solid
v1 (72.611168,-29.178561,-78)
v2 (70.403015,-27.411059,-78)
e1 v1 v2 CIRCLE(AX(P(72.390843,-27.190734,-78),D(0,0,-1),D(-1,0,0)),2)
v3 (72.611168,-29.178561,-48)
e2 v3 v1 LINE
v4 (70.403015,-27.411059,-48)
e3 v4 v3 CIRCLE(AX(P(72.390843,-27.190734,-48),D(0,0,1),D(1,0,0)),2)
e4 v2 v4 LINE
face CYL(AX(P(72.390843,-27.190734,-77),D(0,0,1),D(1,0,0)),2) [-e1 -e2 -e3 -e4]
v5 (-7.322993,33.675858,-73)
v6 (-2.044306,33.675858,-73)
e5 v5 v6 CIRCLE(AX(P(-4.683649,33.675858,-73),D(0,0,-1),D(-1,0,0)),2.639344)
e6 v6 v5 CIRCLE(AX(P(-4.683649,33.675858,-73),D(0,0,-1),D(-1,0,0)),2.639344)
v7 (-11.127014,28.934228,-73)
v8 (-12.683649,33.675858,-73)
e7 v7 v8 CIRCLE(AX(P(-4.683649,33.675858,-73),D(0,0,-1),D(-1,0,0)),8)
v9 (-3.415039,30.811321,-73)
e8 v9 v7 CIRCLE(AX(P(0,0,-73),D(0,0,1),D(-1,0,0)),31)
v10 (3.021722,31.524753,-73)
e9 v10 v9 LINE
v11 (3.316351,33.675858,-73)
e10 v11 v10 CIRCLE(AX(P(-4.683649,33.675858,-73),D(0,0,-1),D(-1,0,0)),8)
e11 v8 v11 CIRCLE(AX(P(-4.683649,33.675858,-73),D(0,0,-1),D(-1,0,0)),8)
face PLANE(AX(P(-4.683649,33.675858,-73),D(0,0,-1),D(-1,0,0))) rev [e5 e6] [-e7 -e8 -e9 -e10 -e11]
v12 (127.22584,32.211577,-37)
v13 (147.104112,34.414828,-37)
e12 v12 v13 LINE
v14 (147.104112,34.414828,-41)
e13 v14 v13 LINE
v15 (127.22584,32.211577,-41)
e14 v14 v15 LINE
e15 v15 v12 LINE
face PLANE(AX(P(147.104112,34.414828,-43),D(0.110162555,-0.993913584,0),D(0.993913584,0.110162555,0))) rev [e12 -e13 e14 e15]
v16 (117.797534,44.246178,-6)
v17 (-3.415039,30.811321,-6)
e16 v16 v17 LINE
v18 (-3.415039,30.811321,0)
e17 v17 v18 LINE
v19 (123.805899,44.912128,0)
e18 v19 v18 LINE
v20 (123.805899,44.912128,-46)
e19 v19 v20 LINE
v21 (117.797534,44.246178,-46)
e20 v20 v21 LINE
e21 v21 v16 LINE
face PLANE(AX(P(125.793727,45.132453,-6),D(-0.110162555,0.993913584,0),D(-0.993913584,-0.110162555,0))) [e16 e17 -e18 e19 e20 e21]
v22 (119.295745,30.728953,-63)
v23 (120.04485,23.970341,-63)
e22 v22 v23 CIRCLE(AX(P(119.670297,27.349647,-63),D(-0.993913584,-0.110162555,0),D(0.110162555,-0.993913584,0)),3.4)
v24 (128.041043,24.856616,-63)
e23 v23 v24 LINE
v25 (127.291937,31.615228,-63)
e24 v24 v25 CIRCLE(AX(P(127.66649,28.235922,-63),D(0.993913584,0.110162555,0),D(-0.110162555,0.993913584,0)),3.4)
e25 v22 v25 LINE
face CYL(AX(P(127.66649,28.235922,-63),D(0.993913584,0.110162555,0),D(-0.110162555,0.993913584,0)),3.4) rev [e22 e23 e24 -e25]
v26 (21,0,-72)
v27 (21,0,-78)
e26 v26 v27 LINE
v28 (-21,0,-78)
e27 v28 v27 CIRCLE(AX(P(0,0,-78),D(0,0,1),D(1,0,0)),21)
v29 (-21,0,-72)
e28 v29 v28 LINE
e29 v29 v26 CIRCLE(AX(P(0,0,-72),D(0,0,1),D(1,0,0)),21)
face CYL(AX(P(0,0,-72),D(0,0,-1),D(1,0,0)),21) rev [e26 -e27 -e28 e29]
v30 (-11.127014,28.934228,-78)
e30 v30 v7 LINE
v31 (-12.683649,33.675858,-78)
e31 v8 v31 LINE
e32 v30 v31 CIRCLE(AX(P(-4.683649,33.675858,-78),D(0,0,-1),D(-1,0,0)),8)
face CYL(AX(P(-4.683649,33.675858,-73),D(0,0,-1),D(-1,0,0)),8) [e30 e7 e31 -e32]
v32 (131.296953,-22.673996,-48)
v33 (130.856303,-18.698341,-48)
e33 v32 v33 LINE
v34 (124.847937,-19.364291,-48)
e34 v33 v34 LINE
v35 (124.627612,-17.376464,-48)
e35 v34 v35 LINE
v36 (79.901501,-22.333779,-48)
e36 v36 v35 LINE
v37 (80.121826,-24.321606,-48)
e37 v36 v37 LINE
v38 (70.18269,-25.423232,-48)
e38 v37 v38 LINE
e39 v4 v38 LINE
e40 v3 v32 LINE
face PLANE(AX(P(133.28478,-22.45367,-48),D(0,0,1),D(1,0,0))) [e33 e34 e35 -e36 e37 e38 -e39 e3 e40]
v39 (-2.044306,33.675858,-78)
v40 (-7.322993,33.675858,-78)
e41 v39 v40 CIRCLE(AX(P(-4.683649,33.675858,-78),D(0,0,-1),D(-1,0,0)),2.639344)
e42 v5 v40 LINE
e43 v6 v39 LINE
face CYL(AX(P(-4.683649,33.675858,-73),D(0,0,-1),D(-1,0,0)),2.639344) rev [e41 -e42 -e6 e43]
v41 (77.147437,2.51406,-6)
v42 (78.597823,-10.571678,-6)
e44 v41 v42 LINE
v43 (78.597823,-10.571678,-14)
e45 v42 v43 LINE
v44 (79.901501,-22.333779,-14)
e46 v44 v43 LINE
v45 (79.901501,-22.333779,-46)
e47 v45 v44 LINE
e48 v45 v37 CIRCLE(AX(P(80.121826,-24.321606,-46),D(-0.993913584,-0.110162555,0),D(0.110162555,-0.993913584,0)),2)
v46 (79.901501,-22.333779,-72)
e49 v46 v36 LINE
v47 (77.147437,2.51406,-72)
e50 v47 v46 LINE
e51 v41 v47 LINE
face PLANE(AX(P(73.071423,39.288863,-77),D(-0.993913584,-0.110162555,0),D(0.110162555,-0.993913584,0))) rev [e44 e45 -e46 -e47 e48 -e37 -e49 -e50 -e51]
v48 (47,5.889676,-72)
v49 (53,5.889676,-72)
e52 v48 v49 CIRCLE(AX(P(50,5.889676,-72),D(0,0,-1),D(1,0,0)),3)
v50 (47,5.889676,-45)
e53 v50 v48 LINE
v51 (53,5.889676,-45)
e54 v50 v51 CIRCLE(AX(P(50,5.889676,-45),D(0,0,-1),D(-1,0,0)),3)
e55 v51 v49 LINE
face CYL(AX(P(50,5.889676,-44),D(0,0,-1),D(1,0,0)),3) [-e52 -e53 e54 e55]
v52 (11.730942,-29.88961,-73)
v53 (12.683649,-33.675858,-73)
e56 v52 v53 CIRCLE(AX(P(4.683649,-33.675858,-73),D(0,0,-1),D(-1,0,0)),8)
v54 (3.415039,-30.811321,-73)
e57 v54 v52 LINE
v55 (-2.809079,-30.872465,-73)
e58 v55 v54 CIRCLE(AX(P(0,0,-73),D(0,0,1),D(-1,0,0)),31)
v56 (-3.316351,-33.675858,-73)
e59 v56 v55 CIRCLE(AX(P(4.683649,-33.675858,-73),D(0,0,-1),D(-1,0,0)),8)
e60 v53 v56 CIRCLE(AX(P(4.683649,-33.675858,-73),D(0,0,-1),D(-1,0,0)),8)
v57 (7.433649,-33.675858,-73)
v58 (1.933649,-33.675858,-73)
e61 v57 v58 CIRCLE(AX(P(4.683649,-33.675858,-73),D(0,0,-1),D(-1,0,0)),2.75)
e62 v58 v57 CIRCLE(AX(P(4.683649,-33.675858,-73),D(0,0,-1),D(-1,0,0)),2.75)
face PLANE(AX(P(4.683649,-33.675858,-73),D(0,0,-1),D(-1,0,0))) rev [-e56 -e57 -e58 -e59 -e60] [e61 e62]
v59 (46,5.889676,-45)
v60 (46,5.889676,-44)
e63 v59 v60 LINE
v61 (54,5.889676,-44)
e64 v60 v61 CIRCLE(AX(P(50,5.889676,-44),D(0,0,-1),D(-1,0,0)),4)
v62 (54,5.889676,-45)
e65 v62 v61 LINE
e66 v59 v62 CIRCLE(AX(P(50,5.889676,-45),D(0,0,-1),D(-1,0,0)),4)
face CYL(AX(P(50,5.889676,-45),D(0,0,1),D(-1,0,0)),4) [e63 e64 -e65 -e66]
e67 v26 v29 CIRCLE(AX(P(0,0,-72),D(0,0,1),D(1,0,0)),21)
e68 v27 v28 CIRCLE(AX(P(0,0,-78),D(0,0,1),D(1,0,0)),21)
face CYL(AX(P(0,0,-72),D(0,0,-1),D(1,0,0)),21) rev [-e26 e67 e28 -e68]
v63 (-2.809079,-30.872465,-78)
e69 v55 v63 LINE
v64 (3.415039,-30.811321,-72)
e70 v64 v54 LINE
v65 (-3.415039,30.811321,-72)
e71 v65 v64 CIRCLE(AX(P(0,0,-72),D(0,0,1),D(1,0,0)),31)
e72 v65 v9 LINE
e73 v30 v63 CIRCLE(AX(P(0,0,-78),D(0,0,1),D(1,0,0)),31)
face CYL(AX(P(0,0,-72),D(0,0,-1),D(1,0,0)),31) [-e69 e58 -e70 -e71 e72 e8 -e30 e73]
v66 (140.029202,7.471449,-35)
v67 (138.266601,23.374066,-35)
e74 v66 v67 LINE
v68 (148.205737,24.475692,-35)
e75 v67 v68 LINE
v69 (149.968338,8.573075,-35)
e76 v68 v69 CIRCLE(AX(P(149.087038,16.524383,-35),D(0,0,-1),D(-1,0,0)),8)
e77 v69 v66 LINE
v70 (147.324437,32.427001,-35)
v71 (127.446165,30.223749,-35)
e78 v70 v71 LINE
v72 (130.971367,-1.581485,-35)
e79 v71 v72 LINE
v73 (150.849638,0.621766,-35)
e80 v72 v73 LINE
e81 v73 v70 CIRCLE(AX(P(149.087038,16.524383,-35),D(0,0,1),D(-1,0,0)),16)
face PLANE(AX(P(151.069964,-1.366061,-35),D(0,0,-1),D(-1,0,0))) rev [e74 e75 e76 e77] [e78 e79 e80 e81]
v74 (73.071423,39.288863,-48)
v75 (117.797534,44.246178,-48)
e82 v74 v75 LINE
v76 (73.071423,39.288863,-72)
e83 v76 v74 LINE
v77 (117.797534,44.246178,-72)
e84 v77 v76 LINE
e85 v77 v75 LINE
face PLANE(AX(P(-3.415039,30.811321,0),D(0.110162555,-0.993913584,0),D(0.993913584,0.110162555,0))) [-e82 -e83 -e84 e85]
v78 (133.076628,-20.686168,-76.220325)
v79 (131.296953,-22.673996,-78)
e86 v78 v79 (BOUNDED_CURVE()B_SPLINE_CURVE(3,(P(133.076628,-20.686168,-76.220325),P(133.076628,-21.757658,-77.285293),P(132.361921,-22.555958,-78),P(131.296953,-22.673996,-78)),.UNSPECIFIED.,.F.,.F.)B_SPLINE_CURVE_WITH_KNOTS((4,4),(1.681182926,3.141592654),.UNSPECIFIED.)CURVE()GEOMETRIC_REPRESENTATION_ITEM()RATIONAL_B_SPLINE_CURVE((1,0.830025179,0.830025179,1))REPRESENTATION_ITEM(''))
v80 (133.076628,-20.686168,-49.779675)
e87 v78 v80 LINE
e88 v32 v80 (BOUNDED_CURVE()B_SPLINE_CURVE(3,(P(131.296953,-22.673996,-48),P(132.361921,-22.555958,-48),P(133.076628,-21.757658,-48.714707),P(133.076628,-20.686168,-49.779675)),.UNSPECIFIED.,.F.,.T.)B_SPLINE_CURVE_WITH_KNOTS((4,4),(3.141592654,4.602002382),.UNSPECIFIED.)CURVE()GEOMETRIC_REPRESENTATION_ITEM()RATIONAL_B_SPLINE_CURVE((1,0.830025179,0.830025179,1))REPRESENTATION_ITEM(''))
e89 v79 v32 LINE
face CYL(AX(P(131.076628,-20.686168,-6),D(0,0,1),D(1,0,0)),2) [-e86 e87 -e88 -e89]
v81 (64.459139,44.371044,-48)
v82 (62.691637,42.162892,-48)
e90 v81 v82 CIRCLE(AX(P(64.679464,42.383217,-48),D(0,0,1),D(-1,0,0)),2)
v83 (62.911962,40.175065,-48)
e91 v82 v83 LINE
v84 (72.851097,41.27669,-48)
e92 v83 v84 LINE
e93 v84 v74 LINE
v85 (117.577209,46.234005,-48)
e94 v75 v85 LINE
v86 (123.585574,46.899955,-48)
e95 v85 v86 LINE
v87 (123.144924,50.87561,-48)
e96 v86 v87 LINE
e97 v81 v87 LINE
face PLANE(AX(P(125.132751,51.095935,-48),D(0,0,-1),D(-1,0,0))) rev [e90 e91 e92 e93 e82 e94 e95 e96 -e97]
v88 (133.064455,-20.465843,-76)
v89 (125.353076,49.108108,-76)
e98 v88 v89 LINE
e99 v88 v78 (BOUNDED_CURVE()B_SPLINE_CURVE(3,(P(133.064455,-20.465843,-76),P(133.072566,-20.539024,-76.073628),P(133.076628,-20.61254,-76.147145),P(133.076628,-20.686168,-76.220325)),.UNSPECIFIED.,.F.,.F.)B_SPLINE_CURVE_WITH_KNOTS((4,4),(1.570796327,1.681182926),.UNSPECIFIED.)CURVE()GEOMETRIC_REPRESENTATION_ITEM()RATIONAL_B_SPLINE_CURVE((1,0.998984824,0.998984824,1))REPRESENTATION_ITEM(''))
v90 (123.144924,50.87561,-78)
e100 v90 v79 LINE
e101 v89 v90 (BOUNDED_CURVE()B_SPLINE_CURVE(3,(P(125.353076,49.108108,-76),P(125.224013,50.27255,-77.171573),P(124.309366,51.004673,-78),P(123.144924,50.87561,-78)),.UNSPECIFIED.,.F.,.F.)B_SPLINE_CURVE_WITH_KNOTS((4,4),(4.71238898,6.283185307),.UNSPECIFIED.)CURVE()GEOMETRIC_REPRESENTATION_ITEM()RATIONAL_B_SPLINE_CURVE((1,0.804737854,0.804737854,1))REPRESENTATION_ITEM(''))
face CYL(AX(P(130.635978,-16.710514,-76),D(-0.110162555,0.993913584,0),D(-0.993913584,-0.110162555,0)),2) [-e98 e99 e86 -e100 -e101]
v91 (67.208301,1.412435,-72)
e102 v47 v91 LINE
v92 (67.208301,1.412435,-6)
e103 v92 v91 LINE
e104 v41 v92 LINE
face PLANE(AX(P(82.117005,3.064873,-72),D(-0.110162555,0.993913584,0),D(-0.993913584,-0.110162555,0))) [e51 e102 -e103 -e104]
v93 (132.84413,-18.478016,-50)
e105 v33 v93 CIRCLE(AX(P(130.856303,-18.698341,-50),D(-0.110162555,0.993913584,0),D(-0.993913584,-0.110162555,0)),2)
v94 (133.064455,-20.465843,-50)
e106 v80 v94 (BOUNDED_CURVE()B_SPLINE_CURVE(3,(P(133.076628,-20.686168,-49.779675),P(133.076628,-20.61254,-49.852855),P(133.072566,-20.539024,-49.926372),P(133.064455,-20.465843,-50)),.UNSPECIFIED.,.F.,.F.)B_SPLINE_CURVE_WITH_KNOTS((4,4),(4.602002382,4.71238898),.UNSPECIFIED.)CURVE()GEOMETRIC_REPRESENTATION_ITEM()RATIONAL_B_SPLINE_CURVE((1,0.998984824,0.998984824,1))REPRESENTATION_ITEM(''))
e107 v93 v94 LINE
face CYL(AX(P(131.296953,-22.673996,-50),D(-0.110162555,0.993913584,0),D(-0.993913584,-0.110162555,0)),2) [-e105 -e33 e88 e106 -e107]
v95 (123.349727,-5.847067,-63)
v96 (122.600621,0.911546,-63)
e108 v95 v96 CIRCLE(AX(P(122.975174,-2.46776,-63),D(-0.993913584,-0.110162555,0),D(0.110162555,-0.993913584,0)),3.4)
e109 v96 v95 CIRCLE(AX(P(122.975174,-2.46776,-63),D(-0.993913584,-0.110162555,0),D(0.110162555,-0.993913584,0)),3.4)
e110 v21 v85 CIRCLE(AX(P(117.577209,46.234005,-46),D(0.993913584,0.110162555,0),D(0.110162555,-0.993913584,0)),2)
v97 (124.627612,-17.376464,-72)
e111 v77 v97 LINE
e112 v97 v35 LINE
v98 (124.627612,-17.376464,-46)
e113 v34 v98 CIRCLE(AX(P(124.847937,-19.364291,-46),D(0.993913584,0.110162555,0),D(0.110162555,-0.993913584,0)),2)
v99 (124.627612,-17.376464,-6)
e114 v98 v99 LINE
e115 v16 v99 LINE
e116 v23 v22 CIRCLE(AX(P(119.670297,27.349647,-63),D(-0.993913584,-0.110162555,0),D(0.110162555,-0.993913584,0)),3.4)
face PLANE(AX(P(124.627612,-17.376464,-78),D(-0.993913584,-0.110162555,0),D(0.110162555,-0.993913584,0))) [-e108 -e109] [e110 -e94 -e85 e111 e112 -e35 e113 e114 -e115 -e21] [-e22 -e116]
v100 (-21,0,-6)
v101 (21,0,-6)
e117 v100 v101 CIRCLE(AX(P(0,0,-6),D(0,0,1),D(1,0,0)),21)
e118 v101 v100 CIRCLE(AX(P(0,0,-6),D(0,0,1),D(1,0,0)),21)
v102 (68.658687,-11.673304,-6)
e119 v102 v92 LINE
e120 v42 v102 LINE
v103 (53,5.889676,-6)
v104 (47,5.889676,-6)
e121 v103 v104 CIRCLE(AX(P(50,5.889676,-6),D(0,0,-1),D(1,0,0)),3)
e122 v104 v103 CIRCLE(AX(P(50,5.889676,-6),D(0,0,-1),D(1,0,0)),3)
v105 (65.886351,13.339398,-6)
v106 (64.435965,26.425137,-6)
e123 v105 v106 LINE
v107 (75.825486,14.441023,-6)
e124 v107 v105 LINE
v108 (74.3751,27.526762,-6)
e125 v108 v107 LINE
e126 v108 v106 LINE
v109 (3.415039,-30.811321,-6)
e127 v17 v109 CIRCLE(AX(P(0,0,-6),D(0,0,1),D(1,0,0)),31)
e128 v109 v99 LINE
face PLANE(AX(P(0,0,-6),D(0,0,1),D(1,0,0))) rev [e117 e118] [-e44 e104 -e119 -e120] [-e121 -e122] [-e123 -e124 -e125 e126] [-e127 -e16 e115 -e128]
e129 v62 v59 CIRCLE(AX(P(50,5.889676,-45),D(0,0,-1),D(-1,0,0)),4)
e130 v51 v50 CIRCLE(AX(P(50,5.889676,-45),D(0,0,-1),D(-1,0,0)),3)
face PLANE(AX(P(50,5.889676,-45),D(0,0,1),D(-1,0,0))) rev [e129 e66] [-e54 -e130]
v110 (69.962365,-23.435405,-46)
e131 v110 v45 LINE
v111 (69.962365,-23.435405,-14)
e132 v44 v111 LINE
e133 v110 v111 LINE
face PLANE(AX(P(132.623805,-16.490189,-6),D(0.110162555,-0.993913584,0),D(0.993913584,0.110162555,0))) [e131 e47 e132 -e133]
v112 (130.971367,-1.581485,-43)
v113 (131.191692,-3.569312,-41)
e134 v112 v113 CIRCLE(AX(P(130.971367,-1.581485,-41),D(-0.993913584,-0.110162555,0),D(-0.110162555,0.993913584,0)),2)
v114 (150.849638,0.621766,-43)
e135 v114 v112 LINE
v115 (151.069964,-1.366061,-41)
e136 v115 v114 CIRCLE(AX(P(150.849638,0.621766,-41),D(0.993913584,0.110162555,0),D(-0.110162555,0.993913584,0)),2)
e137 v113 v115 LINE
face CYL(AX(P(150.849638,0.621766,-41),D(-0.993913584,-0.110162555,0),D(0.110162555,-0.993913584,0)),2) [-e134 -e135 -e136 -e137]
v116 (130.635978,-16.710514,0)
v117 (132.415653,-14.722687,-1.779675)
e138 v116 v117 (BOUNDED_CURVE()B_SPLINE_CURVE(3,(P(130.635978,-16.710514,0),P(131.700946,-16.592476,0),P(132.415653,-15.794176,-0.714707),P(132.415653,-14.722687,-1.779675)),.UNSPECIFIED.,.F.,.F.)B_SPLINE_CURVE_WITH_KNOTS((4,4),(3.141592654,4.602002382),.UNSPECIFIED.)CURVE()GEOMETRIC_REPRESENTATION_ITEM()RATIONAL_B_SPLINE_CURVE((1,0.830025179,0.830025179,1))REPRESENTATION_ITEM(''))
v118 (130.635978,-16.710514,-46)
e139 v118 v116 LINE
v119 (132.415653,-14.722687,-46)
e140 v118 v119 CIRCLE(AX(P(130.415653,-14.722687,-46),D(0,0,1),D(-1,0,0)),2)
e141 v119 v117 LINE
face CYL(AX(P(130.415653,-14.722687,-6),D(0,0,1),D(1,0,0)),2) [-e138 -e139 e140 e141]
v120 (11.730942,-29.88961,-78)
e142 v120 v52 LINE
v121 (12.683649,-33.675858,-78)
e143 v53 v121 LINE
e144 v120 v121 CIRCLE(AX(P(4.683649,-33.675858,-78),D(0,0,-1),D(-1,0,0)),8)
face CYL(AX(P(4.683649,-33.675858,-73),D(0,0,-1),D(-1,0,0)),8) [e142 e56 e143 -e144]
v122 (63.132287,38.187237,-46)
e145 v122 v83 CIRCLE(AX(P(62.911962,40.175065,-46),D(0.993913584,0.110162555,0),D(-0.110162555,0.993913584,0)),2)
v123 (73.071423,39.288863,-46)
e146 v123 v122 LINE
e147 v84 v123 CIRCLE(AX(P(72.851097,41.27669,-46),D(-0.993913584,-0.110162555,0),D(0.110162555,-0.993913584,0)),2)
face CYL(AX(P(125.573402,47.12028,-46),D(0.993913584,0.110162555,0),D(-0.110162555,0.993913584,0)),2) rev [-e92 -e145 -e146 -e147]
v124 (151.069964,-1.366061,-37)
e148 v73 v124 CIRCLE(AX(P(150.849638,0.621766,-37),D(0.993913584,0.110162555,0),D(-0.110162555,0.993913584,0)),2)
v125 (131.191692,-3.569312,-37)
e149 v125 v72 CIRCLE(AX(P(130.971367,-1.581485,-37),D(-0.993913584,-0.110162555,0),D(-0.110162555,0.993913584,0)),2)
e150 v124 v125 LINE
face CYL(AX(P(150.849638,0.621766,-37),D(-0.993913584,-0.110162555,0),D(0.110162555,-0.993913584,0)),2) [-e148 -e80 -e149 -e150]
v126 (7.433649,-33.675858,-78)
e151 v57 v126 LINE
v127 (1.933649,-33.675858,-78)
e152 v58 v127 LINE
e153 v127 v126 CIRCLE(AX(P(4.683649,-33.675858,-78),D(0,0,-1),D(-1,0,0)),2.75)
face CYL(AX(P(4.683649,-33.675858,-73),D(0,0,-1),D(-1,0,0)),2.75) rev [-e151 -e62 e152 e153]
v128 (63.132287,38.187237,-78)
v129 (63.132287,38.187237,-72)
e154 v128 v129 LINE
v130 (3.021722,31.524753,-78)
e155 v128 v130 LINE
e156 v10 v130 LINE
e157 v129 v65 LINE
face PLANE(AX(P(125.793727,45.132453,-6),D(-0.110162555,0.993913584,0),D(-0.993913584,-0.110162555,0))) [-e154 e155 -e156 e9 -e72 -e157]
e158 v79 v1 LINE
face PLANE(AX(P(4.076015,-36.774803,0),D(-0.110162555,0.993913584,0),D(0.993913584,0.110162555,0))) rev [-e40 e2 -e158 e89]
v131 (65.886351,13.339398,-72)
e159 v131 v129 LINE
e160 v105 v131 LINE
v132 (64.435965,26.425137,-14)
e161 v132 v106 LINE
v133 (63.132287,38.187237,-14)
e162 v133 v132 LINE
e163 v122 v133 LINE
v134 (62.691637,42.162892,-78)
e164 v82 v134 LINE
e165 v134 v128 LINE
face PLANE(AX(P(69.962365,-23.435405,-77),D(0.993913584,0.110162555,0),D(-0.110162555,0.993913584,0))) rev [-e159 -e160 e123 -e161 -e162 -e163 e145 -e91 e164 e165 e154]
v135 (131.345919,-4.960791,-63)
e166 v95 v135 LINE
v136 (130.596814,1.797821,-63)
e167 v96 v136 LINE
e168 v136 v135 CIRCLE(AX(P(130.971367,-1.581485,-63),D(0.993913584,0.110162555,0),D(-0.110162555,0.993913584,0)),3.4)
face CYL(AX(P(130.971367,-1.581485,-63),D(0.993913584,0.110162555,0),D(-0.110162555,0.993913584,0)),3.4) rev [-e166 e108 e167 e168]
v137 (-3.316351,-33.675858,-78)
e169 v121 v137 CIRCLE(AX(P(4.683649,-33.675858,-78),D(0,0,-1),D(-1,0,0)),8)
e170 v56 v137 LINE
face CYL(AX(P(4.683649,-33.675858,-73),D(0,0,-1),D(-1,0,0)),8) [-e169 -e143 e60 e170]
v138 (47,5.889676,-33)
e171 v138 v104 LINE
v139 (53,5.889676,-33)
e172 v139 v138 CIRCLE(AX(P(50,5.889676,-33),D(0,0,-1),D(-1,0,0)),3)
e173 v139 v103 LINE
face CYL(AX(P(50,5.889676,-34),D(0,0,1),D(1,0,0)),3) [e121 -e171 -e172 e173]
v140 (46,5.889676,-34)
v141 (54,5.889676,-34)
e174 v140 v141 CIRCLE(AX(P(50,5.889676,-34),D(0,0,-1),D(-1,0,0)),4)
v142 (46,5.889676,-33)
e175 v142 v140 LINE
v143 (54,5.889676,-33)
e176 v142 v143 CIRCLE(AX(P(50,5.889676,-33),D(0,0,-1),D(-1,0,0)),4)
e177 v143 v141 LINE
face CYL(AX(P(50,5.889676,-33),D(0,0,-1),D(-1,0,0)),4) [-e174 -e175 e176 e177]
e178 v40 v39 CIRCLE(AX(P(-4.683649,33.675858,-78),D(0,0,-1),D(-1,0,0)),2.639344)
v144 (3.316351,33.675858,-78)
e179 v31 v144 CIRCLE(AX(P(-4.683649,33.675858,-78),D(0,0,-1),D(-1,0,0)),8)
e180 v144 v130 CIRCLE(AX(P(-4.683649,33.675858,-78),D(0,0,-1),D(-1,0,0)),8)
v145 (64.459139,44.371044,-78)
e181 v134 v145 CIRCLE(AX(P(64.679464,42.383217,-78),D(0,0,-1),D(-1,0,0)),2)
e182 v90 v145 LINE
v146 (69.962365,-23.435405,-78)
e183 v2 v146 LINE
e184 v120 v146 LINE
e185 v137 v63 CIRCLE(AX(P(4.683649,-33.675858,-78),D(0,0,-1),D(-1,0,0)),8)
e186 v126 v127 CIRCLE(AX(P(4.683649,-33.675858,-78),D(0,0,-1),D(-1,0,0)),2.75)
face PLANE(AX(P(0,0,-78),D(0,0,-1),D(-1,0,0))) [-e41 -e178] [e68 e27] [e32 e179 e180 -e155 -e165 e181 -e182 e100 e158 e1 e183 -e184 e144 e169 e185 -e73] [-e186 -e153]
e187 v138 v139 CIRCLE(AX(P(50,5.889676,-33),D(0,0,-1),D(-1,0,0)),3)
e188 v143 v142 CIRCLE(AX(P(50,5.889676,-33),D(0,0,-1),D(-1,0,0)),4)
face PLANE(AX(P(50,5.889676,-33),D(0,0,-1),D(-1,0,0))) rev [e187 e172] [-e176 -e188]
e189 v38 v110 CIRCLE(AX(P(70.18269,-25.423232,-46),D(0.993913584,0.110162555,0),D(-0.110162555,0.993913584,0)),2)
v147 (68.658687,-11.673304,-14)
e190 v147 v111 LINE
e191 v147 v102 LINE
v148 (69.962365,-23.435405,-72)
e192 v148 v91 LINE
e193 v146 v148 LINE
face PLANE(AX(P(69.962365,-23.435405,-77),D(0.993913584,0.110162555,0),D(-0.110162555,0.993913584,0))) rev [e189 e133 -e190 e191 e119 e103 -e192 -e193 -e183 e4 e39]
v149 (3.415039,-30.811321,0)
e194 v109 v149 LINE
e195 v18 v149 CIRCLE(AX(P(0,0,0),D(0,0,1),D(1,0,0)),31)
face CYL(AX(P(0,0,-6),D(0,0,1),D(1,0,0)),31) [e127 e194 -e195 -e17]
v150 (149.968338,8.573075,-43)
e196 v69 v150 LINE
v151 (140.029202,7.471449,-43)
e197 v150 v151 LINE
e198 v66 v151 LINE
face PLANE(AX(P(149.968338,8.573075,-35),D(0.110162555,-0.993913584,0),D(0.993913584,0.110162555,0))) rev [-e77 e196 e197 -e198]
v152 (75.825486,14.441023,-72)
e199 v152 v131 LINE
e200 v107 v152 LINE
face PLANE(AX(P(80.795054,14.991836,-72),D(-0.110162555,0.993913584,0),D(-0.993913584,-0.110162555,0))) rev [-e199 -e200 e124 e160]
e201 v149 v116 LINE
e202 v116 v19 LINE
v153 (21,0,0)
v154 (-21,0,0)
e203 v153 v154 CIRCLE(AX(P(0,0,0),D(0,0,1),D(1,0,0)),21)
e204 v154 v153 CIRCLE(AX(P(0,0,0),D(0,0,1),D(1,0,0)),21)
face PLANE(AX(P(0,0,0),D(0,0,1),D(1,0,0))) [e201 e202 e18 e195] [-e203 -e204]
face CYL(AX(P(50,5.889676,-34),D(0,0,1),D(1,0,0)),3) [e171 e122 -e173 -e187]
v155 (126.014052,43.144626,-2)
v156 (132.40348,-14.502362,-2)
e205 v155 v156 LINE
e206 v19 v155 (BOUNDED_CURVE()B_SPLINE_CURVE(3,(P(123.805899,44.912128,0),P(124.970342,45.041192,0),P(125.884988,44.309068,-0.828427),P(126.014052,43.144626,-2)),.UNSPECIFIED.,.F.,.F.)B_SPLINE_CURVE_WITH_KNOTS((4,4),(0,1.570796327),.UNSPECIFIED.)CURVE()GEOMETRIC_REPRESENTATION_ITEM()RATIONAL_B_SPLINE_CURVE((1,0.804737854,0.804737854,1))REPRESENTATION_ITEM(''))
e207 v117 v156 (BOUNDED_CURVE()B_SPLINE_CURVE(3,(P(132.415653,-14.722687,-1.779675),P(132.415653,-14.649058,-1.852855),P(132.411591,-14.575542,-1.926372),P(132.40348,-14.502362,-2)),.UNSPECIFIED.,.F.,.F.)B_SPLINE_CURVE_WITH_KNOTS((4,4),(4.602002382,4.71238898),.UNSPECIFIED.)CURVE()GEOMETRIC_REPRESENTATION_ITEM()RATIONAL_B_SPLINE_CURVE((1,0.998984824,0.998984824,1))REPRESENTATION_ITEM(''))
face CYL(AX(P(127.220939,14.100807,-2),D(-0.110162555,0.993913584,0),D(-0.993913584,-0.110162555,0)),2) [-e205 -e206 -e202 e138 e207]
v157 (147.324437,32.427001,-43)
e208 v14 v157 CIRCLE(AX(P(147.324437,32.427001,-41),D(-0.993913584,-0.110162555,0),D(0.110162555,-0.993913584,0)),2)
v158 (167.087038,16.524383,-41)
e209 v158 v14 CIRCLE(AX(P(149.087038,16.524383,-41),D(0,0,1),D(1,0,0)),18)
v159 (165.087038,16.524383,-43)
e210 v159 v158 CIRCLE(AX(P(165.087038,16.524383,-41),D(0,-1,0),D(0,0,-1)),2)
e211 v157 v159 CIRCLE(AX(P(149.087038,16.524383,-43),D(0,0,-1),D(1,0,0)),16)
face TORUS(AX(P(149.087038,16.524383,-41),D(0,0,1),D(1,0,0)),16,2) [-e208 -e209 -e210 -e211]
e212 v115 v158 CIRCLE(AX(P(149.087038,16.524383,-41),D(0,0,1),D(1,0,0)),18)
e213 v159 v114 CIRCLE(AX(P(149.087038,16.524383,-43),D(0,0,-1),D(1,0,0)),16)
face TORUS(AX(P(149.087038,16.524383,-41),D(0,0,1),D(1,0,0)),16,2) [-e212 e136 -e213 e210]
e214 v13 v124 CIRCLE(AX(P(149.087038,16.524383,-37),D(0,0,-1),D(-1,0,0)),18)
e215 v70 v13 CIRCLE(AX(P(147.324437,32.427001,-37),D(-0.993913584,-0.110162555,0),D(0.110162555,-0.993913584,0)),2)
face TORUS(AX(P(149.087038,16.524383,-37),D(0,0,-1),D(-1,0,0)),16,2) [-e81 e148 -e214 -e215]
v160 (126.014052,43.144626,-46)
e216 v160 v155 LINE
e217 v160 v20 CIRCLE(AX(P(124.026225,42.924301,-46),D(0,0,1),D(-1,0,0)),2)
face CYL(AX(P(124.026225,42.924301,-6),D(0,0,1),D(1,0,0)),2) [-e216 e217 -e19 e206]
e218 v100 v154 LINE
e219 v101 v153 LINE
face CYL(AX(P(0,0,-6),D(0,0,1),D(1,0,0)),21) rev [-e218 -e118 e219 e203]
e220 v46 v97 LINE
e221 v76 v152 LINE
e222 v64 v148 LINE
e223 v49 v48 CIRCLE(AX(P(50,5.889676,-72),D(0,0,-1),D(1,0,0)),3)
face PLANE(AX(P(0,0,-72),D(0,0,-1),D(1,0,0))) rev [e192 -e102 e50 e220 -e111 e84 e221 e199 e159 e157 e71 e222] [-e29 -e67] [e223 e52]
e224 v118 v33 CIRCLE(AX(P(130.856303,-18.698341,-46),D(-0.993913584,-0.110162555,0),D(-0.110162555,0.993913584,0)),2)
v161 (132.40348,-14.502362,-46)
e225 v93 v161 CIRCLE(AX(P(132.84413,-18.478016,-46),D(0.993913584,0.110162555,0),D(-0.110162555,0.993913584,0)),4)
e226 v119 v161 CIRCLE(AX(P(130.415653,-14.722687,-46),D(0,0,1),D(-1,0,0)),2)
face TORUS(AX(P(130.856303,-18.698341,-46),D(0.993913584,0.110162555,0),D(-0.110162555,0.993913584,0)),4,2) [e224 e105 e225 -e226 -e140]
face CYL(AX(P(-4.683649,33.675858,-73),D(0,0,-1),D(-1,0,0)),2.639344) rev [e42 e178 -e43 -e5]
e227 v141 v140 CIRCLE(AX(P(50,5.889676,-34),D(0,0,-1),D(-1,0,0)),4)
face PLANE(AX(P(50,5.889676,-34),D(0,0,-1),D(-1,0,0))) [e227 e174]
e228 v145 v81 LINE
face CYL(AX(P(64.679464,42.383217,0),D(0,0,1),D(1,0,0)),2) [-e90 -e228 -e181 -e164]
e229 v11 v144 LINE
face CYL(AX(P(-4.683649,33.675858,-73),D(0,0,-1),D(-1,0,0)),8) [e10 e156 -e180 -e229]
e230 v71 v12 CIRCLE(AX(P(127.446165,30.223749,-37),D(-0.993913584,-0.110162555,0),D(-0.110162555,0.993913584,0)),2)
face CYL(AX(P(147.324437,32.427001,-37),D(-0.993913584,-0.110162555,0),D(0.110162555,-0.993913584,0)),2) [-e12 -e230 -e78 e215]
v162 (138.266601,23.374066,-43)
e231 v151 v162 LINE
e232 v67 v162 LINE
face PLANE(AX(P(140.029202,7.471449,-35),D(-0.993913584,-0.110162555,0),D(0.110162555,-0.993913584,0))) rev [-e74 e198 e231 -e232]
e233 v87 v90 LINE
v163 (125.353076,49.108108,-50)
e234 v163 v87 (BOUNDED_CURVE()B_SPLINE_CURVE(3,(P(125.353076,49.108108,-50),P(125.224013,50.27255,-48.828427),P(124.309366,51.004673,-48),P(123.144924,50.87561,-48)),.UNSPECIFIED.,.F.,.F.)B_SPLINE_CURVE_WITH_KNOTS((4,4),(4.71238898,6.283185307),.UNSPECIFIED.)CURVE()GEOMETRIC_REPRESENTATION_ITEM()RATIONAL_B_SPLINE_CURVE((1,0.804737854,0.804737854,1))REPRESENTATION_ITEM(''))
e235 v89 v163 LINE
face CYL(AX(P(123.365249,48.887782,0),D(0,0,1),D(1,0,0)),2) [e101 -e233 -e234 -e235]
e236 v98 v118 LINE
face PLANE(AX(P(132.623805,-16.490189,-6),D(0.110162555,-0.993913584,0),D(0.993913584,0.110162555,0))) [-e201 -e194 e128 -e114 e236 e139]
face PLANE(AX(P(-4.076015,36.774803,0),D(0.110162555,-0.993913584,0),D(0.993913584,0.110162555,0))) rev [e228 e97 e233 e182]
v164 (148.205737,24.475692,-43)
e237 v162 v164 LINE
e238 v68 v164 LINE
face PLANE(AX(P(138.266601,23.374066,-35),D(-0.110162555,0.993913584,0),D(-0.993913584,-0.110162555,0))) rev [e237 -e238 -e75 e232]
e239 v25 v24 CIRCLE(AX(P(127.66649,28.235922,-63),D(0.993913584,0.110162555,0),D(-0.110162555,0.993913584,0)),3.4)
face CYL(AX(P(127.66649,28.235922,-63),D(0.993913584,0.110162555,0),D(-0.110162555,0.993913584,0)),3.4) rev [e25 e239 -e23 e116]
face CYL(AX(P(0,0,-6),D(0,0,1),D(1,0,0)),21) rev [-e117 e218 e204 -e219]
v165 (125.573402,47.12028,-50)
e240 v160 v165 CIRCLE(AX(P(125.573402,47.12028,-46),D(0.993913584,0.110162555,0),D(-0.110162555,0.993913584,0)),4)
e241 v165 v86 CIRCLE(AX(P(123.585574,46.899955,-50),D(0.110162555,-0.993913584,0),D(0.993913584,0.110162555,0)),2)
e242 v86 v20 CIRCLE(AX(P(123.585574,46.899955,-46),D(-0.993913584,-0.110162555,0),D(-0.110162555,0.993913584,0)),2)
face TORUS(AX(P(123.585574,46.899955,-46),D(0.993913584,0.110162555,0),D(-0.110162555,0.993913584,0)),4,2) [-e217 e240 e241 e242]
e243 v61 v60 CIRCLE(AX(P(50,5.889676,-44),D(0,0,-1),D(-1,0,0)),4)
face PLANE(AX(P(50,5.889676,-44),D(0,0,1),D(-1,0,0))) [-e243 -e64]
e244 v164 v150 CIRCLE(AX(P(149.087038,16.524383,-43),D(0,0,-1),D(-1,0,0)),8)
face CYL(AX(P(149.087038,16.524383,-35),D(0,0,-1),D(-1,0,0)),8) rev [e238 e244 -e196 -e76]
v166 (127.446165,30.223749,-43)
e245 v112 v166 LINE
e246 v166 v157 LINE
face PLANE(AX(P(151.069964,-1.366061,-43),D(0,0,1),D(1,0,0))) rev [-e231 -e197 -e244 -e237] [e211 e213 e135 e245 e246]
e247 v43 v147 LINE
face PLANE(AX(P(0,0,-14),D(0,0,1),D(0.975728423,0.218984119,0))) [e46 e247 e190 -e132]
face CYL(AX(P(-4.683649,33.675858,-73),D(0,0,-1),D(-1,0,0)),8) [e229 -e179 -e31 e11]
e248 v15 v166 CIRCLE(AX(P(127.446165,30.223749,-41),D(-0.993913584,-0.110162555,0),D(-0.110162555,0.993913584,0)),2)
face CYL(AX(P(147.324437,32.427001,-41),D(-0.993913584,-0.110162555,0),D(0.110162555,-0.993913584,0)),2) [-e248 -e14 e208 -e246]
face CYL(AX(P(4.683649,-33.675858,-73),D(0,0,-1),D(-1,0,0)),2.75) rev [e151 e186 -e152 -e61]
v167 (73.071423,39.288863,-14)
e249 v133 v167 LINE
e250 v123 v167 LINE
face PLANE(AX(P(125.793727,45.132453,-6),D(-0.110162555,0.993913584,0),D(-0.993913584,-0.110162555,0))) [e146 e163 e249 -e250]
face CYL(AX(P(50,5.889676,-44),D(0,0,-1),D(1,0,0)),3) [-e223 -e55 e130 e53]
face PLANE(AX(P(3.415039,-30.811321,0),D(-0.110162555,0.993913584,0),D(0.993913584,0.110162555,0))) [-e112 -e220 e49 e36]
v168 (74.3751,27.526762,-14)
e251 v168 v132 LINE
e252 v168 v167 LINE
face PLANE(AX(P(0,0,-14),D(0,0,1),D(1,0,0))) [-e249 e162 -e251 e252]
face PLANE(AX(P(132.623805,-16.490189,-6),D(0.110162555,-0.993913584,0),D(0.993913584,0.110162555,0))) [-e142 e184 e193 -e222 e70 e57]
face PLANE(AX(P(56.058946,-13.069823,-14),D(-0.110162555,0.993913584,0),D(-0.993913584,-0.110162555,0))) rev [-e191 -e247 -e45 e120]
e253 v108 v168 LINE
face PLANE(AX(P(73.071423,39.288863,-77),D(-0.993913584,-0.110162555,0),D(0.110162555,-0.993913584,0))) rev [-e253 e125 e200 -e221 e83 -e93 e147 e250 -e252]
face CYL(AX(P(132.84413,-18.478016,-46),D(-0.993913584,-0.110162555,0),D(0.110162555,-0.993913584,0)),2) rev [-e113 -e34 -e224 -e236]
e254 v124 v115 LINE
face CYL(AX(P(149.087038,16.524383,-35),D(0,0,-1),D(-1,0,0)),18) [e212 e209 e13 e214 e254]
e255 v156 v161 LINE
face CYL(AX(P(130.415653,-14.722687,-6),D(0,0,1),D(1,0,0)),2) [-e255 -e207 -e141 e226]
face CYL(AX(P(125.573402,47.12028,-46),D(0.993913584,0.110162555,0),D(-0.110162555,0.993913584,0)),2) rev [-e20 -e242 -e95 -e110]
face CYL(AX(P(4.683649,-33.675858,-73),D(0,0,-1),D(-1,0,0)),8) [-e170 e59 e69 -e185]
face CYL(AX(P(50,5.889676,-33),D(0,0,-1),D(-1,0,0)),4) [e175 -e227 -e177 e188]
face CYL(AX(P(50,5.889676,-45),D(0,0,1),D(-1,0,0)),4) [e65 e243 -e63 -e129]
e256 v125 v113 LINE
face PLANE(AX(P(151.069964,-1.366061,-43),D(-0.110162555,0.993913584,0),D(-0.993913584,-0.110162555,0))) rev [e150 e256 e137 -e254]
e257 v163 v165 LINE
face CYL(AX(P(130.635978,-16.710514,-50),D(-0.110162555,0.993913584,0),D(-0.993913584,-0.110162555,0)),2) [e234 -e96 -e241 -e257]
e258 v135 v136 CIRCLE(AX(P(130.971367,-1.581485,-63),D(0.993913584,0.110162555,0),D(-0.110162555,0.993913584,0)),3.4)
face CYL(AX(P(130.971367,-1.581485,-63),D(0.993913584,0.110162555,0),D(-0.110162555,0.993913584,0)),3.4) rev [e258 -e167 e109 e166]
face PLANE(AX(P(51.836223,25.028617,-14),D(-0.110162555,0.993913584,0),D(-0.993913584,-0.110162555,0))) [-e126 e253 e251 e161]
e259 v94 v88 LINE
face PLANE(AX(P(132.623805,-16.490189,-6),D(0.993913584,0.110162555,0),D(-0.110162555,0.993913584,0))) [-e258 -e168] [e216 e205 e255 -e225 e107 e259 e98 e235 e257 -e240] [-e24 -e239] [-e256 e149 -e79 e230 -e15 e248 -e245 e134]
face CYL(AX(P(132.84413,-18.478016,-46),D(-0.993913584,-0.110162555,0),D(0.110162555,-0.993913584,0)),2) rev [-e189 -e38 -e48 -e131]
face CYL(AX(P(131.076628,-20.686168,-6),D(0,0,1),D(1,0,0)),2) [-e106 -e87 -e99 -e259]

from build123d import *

# Parameters (mm, degrees)
SKETCH1_R                   = 21
BOSS_EXTRUDE1_DEPTH         = 6
BOSS_EXTRUDE2_DEPTH         = 78
SKETCH3_R                   = 3.0000000000000013
BOSS_EXTRUDE3_DEPTH         = 28
BOSS_EXTRUDE4_DEPTH         = 71.00000000000003
SKETCH10_R                  = 3.9999999999999982
BOSS_EXTRUDE6_DEPTH         = 1
CUT_EXTRUDE1_DEPTH          = 8
SKETCH8_W                   = 66
SKETCH8_H                   = 6.000000000000007
CUT_EXTRUDE3_DEPTH          = 15
BOSS_EXTRUDE7_DEPTH         = 6
FILLET2_R                   = 2
TAP_DRILL_FOR_M8_TAP1_D     = 6.8
TAP_DRILL_FOR_M8_TAP1_DEPTH = 20
TAP_DRILL_FOR_M8_TAP1_TIP   = 2.042926104693705
SKETCH14_R                  = 8
SKETCH14_R_2                = 2.6393435591760683
SKETCH14_R_3                = 2.7500000000000004
BOSS_EXTRUDE8_DEPTH         = 5
BOSS_EXTRUDE9_DEPTH         = 20
SKETCH16_R                  = 17.999999999999996
BOSS_EXTRUDE10_DEPTH        = 8
CUT_EXTRUDE4_DEPTH          = 8
FILLET3_R                   = 2


with BuildPart() as part:
    # Sketch1 → Boss-Extrude1 (new body)
    with BuildSketch(Plane.XY):
        with BuildLine():
            Line((132.62380505793305, -16.490188960571935), (3.41503919990868, -30.811321089221206))
            ThreePointArc((3.41503919990868, -30.811321089221206), (-30.81132108922119, -3.4150391999086844), (-3.415039199908666, 30.811321089221195))
            Line((-3.415039199908666, 30.811321089221195), (125.79372665811573, 45.132453217870456))
            Line((125.79372665811573, 45.132453217870456), (132.62380505793305, -16.490188960571935))
        make_face()
        Circle(SKETCH1_R, mode=Mode.SUBTRACT)
    extrude(amount=-BOSS_EXTRUDE1_DEPTH)

    # Sketch2 → Boss-Extrude2 (add)
    with BuildSketch(Plane.XY):
        Polygon((125.79372665811573, 45.132453217870456), (132.62380505793305, -16.49018896057193), (124.62761225366665, -17.376464229247457), (117.79753385384927, 44.24617794919492), align=None)
    extrude(amount=-BOSS_EXTRUDE2_DEPTH)

    # Sketch3 → Boss-Extrude3 (add)
    with BuildSketch(Plane(origin=(0, 0, -6), x_dir=(-1, 0, 0), z_dir=(0, 0, -1))):
        with Locations(Location((-50.00000000000005, 5.889675971997146, 0), (0, 0, 180))):
            Circle(SKETCH3_R)
    extrude(amount=BOSS_EXTRUDE3_DEPTH)

    # Sketch4 → Boss-Extrude4 (add)
    with BuildSketch(Plane(origin=(0, 0, -6), x_dir=(-1, 0, 0), z_dir=(0, 0, -1))):
        Polygon((-73.07142259530238, 39.28886298158555), (-79.90150099511973, -22.333779196856817), (-69.96236515988706, -23.435404745214456), (-63.132286760069725, 38.187237433227914), align=None)
    extrude(amount=BOSS_EXTRUDE4_DEPTH)

    # Sketch10 → Boss-Extrude6 (add)
    with BuildSketch(Plane(origin=(0, 0, -34), x_dir=(-1, 0, 0), z_dir=(0, 0, -1))):
        with Locations((-50.00000000000005, 5.889675971997146)):
            Circle(SKETCH10_R)
    extrude(amount=-BOSS_EXTRUDE6_DEPTH)

    # Mirror1: part across plane


with BuildPart() as part_1:
    add(part.part)
    add(part.part.mirror(Plane.XY.offset(-39)))

    # Sketch6 → Cut-Extrude1 (cut)
    with BuildSketch(Plane(origin=(0, 0, -6), x_dir=(-1, 0, 0), z_dir=(0, 0, -1))):
        Polygon((-77.79892131409314, 39.8128454942288), (-50.532545288662256, 36.79071792311109), (-51.836223102446034, 25.02861700243648), (-77.79892131409314, 27.90624863242818), align=None)
    cut_extrude1 = extrude(amount=CUT_EXTRUDE1_DEPTH, mode=Mode.SUBTRACT)

    # Mirror4: Cut-Extrude1 across plane
    add(cut_extrude1.mirror(Plane(origin=(0, 0, 0), x_dir=(0, 0, 1), z_dir=(-0.11016255483576362, 0.9939135835232646, 0))), mode=Mode.SUBTRACT)

    # Sketch8 → Cut-Extrude3 (cut)
    with BuildSketch(Plane(origin=(66.54732595997841, 7.375916344006741, 0), x_dir=(0, 0, 1), z_dir=(-0.9939135835232656, -0.1101625548357545, 0))):
        with Locations((-39, 2.9999999999999964)):
            Rectangle(SKETCH8_W, SKETCH8_H)
    cut_extrude3 = extrude(amount=-CUT_EXTRUDE3_DEPTH, mode=Mode.SUBTRACT)

    # Mirror5: Cut-Extrude3 across plane
    add(cut_extrude3.mirror(Plane(origin=(81.45602971282739, 9.02835466654305, -72), x_dir=(0, 0, 1), z_dir=(0.1101625548357545, -0.9939135835232656, 0))), mode=Mode.SUBTRACT)

    # Sketch11 → Boss-Extrude7 (add)
    with BuildSketch(Plane(origin=(-3.41503919990867, 30.811321089221206, 0), x_dir=(0.9939135835232645, 0.11016255483576355, 0), z_dir=(-0.11016255483576357, 0.9939135835232646, 0))):
        Polygon((129.99999999999997, 78), (66.95484100748354, 78), (66.95484100748354, 47.99999999999999), (129.99999999999997, 48), align=None)
    boss_extrude7 = extrude(amount=BOSS_EXTRUDE7_DEPTH)

    # Mirror6: Boss-Extrude7 across plane
    add(boss_extrude7.mirror(Plane(origin=(0, 0, 0), x_dir=(0, 0, 1), z_dir=(-0.11016255483576362, 0.9939135835232646, 0))))

    # Fillet2
    fillet2_edges = [part_1.edges().sort_by_distance(p)[0] for p in [
        (129.20876585802438, 14.321132128649257, -78),
        (125.79372665811574, 45.132453217870456, -24),
        (125.46323899360841, 48.114193968440254, -48),
        (68.10185467768603, 38.73805020740676, -47.99999999999999),
        (121.79563025598249, 44.689315583532704, -48),
        (125.13275132910113, 51.09593471901005, -63),
        (62.47131143105514, 44.15071893436753, -63),
        (132.62380505793305, -16.49018896057193, -24),
        (133.28478038694766, -22.45367046171154, -63),
        (132.95429272244036, -19.471929711141737, -48),
        (70.62334048890166, -29.39888624635408, -63),
        (74.9319330775034, -22.884591971035665, -47.99999999999999),
        (128.62570865579985, -16.933326594909712, -48),
        (129.20876585802438, 14.32113212864926, 0),
    ]]
    fillet(fillet2_edges, radius=FILLET2_R)

    # Tap Drill for M8 Tap1
    with Locations(Plane(origin=(129.2087658580244, 14.321132128649255, 0), x_dir=(0, 0, -1), z_dir=(0.9939135835232646, 0.11016255483576352, 0))):
        with Locations((63, 14), (63, -16)):
            Hole(TAP_DRILL_FOR_M8_TAP1_D / 2, depth=TAP_DRILL_FOR_M8_TAP1_DEPTH)
            with Locations((0, 0, -(TAP_DRILL_FOR_M8_TAP1_DEPTH + TAP_DRILL_FOR_M8_TAP1_TIP / 2))):  # 118° drill point
                Cone(0, TAP_DRILL_FOR_M8_TAP1_D / 2, TAP_DRILL_FOR_M8_TAP1_TIP, mode=Mode.SUBTRACT)

    # Sketch14 → Boss-Extrude8 (add)
    # profile 1 of 2: a face of its own
    with BuildSketch(Plane(origin=(0, 0, -78), x_dir=(-1, 0, 0), z_dir=(0, 0, -1))):
        with Locations((4.683649461628586, 33.67585823287338)):
            Circle(SKETCH14_R)
        with Locations((4.683649461628586, 33.67585823287338)):
            Circle(SKETCH14_R_2, mode=Mode.SUBTRACT)
    # profile 2 of 2: a face of its own
    with BuildSketch(Plane(origin=(0, 0, -78), x_dir=(-1, 0, 0), z_dir=(0, 0, -1))):
        with Locations((-4.683649461628697, -33.675858232873395)):
            Circle(SKETCH14_R)
        with Locations((-4.683649461628697, -33.675858232873395)):
            Circle(SKETCH14_R_3, mode=Mode.SUBTRACT)
    extrude(amount=-BOSS_EXTRUDE8_DEPTH)

    # Sketch15 → Boss-Extrude9 (add)
    with BuildSketch(Plane(origin=(129.2087658580244, 14.321132128649255, 0), x_dir=(0, 0, -1), z_dir=(0.9939135835232646, 0.11016255483576352, 0))):
        Polygon((43, -17.999999999999993), (34.999999999999865, -18), (34.999999999999865, 18), (43, 18.000000000000007), align=None)
    extrude(amount=BOSS_EXTRUDE9_DEPTH)

    # Sketch16 → Boss-Extrude10 (add)
    with BuildSketch(Plane(origin=(0, 0, -43), x_dir=(-1, 0, 0), z_dir=(0, 0, -1))):
        with Locations((-149.0870375284897, 16.524383225364534)):
            Circle(SKETCH16_R)
    extrude(amount=-BOSS_EXTRUDE10_DEPTH)

    # Sketch17 → Cut-Extrude4 (cut)
    with BuildSketch(Plane(origin=(0, 0, -43), x_dir=(-1, 0, 0), z_dir=(0, 0, -1))):
        with BuildLine():
            Line((-138.26660125457093, 23.374066345193015), (-148.20573708980362, 24.475691893550643))
            ThreePointArc((-148.20573708980362, 24.475691893550643), (-157.0383461966758, 17.40568366405063), (-149.9683379671758, 8.573074557178417))
            Line((-149.9683379671758, 8.573074557178417), (-140.02920213194318, 7.471449008820779))
            Line((-140.02920213194318, 7.471449008820779), (-138.26660125457093, 23.374066345193015))
        make_face()
    extrude(amount=-CUT_EXTRUDE4_DEPTH, mode=Mode.SUBTRACT)

    # Fillet3
    fillet3_edges = [part_1.edges().sort_by_distance(p)[0] for p in [
        (137.1649757062133, 33.31320218042565, -34.999999999999865),
        (141.1308276803008, -2.4676868264118728, -34.999999999999865),
        (141.13082768030077, -2.4676868264118657, -43),
        (137.1649757062133, 33.31320218042566, -43),
        (166.97748203190847, 18.507309212408288, -35),
        (166.97748203190847, 18.507309212408288, -43),
    ]]
    fillet(fillet3_edges, radius=FILLET3_R)


solid = part_1.part
